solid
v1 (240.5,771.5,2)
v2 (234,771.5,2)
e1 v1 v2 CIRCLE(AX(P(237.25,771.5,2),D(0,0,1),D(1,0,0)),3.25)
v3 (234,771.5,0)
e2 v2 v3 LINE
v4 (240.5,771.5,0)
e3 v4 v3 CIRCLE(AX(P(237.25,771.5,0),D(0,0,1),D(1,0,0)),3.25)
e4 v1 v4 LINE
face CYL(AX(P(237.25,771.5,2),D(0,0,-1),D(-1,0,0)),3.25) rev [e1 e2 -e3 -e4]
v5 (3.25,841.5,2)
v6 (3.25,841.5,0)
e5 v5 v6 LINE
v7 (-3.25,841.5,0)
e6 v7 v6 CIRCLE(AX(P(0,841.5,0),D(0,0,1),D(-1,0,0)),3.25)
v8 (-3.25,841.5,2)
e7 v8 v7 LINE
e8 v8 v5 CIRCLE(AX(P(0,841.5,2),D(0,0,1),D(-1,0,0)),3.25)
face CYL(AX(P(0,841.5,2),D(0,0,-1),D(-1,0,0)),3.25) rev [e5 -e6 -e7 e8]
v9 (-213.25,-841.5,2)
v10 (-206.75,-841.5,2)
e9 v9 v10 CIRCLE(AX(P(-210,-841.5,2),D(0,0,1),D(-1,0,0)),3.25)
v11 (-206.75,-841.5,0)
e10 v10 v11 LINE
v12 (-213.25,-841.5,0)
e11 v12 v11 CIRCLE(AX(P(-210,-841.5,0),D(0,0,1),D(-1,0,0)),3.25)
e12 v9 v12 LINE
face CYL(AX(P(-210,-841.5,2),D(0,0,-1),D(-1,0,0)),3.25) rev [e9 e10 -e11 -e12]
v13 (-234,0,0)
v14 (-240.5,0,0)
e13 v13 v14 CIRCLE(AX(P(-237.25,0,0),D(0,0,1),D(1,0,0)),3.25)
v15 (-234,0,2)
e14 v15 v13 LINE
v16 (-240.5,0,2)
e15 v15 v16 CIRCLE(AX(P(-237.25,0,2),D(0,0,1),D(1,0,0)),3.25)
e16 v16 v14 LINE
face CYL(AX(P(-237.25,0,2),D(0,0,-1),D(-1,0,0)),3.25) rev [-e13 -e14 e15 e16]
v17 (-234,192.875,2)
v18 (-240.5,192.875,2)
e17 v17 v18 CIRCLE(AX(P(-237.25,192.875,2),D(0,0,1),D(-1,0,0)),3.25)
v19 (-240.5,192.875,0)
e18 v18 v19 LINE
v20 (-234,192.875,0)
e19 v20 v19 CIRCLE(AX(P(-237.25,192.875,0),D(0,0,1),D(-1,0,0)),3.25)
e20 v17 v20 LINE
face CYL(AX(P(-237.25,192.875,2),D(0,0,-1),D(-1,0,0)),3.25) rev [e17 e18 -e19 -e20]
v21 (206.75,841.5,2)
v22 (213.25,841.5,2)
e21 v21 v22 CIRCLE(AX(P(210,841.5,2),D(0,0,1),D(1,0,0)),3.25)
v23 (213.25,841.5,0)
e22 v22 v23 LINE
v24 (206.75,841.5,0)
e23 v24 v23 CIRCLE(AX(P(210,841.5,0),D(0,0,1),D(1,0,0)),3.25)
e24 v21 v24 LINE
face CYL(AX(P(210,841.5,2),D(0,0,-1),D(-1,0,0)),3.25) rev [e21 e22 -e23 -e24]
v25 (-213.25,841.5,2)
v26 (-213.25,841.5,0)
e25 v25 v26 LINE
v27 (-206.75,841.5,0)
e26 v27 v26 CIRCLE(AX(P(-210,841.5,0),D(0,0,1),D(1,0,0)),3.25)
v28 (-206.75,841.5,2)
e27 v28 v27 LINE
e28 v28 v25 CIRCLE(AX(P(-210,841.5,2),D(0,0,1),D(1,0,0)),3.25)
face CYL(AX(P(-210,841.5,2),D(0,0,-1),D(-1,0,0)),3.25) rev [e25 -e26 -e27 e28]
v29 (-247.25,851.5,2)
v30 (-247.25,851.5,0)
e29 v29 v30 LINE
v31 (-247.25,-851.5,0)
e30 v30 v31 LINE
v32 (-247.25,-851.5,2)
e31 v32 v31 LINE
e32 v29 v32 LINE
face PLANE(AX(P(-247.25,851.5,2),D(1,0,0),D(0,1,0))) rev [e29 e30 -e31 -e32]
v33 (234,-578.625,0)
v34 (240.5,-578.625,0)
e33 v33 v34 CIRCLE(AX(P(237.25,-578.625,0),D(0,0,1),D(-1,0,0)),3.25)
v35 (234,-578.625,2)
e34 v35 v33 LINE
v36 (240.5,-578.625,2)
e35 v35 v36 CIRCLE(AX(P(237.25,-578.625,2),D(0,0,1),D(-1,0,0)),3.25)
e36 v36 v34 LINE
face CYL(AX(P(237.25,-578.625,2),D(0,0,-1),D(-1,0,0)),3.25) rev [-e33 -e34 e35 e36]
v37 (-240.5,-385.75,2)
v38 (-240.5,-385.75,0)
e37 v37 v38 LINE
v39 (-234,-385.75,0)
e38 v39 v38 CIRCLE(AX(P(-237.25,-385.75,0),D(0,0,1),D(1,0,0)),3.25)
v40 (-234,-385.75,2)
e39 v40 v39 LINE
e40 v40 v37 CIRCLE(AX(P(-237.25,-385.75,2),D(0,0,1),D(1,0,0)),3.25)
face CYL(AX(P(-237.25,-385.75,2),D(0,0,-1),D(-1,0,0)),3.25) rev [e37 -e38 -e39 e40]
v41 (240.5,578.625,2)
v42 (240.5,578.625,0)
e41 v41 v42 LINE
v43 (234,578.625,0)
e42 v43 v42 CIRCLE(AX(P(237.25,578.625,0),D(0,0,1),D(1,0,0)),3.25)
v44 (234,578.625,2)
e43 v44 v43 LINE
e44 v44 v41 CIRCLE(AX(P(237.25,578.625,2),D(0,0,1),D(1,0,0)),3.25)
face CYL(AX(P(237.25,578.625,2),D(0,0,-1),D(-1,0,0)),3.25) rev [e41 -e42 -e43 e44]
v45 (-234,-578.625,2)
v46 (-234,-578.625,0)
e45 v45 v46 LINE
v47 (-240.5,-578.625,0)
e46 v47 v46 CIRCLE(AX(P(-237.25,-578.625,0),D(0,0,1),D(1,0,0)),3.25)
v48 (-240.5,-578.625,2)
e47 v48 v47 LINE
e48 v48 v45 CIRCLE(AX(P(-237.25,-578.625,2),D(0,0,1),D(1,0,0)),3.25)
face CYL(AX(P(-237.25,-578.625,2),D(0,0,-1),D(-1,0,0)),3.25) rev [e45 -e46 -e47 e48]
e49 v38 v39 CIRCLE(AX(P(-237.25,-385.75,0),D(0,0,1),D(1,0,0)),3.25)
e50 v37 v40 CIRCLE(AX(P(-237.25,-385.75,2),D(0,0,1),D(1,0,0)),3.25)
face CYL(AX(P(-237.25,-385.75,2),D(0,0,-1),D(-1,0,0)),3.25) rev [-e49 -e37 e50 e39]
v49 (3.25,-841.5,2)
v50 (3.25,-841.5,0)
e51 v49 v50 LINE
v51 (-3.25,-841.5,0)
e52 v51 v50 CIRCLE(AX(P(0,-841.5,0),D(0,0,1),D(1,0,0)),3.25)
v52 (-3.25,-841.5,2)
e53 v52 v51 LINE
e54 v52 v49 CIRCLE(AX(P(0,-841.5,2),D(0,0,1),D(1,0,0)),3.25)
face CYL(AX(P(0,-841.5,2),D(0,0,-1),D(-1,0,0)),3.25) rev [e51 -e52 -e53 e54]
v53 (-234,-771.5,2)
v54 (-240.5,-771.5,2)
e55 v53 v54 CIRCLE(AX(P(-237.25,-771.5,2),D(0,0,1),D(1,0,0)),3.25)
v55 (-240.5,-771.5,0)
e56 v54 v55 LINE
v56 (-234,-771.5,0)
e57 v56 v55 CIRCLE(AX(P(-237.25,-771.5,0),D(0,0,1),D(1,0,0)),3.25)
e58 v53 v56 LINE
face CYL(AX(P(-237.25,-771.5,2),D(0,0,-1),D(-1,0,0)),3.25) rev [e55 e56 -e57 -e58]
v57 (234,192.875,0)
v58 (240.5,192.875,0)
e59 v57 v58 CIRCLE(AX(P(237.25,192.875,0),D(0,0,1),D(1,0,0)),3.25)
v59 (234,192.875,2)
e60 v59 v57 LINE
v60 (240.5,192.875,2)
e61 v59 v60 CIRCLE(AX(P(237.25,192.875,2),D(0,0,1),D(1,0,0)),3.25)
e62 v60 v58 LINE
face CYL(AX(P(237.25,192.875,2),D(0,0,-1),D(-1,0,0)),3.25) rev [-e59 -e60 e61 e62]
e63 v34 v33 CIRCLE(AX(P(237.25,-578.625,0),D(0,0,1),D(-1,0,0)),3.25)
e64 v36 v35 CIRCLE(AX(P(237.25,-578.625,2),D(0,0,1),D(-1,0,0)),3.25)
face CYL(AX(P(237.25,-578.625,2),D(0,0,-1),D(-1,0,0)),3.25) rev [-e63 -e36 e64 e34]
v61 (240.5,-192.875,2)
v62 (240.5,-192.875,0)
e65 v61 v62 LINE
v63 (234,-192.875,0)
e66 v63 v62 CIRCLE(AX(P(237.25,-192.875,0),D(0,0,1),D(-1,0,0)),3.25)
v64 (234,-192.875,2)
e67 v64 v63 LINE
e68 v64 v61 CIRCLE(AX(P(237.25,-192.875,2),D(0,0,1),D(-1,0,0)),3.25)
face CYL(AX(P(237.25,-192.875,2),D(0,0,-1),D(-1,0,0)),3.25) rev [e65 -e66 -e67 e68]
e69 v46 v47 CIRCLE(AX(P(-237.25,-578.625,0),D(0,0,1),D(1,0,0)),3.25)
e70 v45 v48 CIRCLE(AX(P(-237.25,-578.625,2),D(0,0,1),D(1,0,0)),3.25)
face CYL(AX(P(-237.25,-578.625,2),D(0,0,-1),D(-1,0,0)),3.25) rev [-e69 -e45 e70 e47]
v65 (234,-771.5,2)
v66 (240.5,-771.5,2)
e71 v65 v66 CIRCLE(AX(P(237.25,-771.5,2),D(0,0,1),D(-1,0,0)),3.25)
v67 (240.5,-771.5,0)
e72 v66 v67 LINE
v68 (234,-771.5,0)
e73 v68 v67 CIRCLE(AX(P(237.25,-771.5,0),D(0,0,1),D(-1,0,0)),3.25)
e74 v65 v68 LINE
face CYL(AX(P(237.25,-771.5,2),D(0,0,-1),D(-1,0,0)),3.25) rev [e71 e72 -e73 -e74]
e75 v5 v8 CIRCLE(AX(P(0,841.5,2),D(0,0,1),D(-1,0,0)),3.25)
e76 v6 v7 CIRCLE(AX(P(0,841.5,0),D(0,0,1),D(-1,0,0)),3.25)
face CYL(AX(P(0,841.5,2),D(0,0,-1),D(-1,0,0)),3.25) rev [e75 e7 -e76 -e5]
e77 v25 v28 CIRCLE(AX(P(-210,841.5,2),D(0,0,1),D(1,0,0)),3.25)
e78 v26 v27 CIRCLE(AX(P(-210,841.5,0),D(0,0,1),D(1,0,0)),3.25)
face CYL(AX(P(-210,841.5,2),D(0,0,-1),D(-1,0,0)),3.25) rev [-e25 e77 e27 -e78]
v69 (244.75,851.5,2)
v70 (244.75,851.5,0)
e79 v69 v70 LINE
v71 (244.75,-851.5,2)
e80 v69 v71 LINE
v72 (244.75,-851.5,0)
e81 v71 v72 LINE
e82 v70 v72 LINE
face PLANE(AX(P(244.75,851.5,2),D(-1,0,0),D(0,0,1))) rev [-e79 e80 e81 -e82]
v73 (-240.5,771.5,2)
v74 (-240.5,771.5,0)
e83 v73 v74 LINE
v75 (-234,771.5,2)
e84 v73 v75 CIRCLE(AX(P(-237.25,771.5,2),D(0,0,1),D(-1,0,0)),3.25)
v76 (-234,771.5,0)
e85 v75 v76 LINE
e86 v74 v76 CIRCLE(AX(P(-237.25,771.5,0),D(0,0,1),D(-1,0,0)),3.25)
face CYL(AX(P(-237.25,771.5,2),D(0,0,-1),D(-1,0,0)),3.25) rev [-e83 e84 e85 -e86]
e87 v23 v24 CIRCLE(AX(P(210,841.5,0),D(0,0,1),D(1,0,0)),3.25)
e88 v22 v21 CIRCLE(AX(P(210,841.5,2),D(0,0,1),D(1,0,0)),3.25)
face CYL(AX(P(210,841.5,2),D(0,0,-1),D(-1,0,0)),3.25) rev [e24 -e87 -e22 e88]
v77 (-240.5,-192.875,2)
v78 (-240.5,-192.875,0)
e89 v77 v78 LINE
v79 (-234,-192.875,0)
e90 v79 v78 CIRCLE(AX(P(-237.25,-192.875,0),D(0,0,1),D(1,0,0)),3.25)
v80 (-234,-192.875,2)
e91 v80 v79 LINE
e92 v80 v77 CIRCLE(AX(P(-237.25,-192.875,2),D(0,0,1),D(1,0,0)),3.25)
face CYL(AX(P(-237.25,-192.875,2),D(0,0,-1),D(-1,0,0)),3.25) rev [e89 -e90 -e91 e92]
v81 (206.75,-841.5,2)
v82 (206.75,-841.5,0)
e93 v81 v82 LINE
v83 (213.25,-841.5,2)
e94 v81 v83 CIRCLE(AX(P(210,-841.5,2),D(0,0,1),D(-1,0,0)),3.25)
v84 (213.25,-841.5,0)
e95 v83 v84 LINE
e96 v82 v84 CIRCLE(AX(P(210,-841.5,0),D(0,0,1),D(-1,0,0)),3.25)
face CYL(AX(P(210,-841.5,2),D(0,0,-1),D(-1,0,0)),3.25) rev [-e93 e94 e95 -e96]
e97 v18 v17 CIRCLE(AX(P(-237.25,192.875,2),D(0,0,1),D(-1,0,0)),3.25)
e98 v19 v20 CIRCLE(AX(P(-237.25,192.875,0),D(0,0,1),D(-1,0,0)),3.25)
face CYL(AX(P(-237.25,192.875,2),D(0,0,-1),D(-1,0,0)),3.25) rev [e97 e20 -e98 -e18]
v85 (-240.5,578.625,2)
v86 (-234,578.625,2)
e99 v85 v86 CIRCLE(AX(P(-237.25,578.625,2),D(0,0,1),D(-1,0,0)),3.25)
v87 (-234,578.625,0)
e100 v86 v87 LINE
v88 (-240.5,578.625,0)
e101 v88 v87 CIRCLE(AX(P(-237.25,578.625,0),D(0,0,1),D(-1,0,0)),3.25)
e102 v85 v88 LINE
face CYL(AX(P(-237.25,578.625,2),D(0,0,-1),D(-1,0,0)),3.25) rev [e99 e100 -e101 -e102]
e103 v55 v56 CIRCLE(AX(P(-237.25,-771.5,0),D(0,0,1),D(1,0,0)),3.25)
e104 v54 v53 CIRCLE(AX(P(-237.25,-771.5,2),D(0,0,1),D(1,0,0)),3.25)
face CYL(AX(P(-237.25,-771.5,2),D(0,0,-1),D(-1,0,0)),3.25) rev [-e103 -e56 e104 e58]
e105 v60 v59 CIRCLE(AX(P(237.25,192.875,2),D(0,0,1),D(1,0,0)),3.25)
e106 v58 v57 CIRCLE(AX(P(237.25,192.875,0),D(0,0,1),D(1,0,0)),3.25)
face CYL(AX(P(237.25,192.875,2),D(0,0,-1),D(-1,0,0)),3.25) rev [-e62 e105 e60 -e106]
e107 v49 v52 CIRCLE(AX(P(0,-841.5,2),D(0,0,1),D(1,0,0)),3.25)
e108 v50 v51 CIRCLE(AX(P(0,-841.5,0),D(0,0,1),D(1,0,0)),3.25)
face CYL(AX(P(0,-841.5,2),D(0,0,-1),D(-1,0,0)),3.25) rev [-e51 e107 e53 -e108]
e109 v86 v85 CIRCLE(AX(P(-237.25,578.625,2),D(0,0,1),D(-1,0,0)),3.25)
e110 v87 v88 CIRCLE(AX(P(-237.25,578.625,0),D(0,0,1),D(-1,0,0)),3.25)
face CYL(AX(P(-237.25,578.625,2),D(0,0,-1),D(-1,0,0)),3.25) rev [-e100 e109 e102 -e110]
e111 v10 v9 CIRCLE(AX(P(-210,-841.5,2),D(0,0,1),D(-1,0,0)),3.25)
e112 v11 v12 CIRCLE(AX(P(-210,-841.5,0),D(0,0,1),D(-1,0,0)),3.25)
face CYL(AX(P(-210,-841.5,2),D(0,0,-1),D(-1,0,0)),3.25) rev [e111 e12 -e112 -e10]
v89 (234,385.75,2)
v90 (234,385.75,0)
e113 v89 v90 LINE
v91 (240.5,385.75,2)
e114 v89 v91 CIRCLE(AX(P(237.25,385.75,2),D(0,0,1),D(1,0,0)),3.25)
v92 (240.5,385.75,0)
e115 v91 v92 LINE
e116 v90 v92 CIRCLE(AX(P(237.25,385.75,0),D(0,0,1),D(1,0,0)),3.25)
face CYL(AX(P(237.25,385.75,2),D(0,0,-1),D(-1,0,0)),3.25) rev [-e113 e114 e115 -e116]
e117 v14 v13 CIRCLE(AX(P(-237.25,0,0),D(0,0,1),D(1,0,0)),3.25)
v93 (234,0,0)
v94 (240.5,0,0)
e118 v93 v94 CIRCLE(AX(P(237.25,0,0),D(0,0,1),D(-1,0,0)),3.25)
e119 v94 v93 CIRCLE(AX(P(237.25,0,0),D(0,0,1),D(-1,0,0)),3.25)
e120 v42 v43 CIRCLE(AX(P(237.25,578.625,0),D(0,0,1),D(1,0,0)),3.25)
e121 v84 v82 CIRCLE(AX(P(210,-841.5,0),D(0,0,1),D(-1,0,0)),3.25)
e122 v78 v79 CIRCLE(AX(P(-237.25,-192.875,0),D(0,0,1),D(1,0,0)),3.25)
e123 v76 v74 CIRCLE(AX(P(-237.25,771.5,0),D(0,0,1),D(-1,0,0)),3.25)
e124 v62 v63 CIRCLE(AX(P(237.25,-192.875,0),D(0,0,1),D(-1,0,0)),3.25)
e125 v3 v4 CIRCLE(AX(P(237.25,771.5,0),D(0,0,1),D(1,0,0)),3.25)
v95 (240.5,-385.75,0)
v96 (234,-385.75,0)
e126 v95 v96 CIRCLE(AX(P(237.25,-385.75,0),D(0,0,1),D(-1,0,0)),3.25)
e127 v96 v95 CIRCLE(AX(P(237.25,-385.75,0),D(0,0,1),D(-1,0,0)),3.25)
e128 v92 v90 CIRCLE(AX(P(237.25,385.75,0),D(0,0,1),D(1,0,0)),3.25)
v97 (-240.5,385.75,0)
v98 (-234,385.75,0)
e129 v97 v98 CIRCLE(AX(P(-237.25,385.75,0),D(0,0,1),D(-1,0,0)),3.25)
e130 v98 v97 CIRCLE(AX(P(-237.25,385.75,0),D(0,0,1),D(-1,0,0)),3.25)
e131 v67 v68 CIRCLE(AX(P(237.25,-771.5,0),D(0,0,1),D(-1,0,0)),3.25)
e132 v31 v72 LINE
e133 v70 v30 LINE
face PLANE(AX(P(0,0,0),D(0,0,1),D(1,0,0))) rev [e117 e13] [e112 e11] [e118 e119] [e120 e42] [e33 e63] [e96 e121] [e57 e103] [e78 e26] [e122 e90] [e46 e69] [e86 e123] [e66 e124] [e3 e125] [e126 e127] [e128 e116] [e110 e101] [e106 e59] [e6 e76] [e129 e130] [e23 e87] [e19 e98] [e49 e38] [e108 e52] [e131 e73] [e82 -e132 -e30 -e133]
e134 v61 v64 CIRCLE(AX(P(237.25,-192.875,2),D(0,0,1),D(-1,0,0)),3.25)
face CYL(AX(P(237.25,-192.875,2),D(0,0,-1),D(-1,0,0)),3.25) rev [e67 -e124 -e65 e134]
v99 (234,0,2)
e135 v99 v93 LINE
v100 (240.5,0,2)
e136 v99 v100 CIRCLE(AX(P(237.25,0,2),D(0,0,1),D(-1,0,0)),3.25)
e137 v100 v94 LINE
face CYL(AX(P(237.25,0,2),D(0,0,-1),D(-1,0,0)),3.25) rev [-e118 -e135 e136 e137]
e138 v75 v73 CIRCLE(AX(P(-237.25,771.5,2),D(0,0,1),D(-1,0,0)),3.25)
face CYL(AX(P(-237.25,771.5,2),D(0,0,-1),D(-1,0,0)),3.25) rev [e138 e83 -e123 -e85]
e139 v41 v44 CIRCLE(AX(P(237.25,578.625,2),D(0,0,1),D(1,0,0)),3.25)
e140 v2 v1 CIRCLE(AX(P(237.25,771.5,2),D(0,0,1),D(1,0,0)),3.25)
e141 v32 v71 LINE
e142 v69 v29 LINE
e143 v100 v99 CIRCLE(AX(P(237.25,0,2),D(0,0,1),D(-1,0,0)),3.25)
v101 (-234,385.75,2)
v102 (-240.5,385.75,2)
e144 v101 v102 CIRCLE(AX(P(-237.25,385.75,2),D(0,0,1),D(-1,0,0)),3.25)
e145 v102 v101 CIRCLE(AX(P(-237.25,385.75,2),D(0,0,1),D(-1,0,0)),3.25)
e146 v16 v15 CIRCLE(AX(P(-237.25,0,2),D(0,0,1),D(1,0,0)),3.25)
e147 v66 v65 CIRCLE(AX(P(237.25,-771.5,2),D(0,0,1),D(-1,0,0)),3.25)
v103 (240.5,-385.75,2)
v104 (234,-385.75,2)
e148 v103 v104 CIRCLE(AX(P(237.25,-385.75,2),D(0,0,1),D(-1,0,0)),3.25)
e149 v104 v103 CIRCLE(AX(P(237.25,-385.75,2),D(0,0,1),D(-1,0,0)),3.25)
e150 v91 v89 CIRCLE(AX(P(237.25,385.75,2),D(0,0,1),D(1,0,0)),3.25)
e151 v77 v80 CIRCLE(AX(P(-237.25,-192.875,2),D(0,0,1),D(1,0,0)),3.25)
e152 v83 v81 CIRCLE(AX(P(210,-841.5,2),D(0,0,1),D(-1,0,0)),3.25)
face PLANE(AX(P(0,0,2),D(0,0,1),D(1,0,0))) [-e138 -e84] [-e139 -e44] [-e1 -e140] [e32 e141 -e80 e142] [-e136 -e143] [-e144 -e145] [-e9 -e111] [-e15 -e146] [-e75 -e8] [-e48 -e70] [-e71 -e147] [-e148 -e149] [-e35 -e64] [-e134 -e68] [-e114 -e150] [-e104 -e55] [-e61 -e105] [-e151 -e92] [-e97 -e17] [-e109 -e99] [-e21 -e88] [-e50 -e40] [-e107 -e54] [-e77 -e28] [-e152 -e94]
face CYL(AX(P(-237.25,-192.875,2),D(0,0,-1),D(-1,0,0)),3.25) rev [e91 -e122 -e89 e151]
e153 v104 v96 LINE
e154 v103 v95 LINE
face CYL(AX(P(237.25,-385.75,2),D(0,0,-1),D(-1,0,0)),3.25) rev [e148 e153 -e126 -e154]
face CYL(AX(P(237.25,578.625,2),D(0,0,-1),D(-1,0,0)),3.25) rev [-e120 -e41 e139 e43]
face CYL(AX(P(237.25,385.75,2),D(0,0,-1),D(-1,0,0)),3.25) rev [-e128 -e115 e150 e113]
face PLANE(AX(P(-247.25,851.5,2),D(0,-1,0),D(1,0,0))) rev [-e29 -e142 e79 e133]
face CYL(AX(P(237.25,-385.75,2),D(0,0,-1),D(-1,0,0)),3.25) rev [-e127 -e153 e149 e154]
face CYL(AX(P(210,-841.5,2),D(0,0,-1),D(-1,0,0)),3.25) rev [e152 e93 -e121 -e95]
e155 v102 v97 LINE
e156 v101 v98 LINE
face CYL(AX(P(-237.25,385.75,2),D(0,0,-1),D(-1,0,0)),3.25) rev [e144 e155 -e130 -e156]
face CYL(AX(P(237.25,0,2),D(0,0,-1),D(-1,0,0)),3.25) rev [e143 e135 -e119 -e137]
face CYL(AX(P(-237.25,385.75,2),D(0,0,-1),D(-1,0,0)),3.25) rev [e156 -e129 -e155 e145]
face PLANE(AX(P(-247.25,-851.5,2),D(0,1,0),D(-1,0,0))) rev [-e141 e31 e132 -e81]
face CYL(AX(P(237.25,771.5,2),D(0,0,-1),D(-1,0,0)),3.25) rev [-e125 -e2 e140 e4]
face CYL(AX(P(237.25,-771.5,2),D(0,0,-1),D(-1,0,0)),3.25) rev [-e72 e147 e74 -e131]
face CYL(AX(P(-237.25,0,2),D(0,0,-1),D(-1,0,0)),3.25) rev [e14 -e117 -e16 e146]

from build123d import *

# Parameters (mm, degrees)
SKETCH_1_W          = 494.5
SKETCH_1_H          = 1703
SKETCH_1_R          = 3.25
EXTRUDE_1_DEPTH     = 2
SKETCH_2_W          = 2.5
SKETCH_2_H          = 2
CUT_EXTRUDE_1_DEPTH = 1721.856055137


with BuildPart() as part:
    # 草图1 → 凸台-拉伸1 (new body)
    with BuildSketch(Plane.XY):
        Rectangle(SKETCH_1_W, SKETCH_1_H)
        with Locations((-237.25, 0)):
            Circle(SKETCH_1_R, mode=Mode.SUBTRACT)
        with Locations((-237.25, -192.875)):
            Circle(SKETCH_1_R, mode=Mode.SUBTRACT)
        with Locations((-237.25, -385.75)):
            Circle(SKETCH_1_R, mode=Mode.SUBTRACT)
        with Locations((-237.25, -578.625)):
            Circle(SKETCH_1_R, mode=Mode.SUBTRACT)
        with Locations((-237.25, -771.5)):
            Circle(SKETCH_1_R, mode=Mode.SUBTRACT)
        with Locations((0, -841.5)):
            Circle(SKETCH_1_R, mode=Mode.SUBTRACT)
        with Locations(Location((0, 841.5, 0), (0, 0, 180))):
            Circle(SKETCH_1_R, mode=Mode.SUBTRACT)
        with Locations(Location((-237.25, 771.5, 0), (0, 0, 180))):
            Circle(SKETCH_1_R, mode=Mode.SUBTRACT)
        with Locations(Location((-237.25, 578.625, 0), (0, 0, 180))):
            Circle(SKETCH_1_R, mode=Mode.SUBTRACT)
        with Locations(Location((-237.25, 385.75, 0), (0, 0, 180))):
            Circle(SKETCH_1_R, mode=Mode.SUBTRACT)
        with Locations(Location((-237.25, 192.875, 0), (0, 0, 180))):
            Circle(SKETCH_1_R, mode=Mode.SUBTRACT)
        with Locations((237.25, 192.875)):
            Circle(SKETCH_1_R, mode=Mode.SUBTRACT)
        with Locations((237.25, 385.75)):
            Circle(SKETCH_1_R, mode=Mode.SUBTRACT)
        with Locations((237.25, 578.625)):
            Circle(SKETCH_1_R, mode=Mode.SUBTRACT)
        with Locations((237.25, 771.5)):
            Circle(SKETCH_1_R, mode=Mode.SUBTRACT)
        with Locations(Location((237.25, -771.5, 0), (0, 0, 180))):
            Circle(SKETCH_1_R, mode=Mode.SUBTRACT)
        with Locations(Location((237.25, -578.625, 0), (0, 0, 180))):
            Circle(SKETCH_1_R, mode=Mode.SUBTRACT)
        with Locations(Location((237.25, -385.75, 0), (0, 0, 180))):
            Circle(SKETCH_1_R, mode=Mode.SUBTRACT)
        with Locations(Location((237.25, -192.875, 0), (0, 0, 180))):
            Circle(SKETCH_1_R, mode=Mode.SUBTRACT)
        with Locations(Location((237.25, 0, 0), (0, 0, 180))):
            Circle(SKETCH_1_R, mode=Mode.SUBTRACT)
        with Locations((-210, 841.5)):
            Circle(SKETCH_1_R, mode=Mode.SUBTRACT)
        with Locations((210, 841.5)):
            Circle(SKETCH_1_R, mode=Mode.SUBTRACT)
        with Locations(Location((-210, -841.5, 0), (0, 0, 180))):
            Circle(SKETCH_1_R, mode=Mode.SUBTRACT)
        with Locations(Location((210, -841.5, 0), (0, 0, 180))):
            Circle(SKETCH_1_R, mode=Mode.SUBTRACT)
    extrude(amount=EXTRUDE_1_DEPTH)

    # 草图2 → 切除-拉伸1 (cut, through all)
    with BuildSketch(Plane(origin=(0, -851.5, 0), x_dir=(-1, 0, 0), z_dir=(0, -1, 0))):
        with Locations((-246, -1)):
            Rectangle(SKETCH_2_W, SKETCH_2_H)
    extrude(amount=-CUT_EXTRUDE_1_DEPTH, mode=Mode.SUBTRACT)


solid = part.part
